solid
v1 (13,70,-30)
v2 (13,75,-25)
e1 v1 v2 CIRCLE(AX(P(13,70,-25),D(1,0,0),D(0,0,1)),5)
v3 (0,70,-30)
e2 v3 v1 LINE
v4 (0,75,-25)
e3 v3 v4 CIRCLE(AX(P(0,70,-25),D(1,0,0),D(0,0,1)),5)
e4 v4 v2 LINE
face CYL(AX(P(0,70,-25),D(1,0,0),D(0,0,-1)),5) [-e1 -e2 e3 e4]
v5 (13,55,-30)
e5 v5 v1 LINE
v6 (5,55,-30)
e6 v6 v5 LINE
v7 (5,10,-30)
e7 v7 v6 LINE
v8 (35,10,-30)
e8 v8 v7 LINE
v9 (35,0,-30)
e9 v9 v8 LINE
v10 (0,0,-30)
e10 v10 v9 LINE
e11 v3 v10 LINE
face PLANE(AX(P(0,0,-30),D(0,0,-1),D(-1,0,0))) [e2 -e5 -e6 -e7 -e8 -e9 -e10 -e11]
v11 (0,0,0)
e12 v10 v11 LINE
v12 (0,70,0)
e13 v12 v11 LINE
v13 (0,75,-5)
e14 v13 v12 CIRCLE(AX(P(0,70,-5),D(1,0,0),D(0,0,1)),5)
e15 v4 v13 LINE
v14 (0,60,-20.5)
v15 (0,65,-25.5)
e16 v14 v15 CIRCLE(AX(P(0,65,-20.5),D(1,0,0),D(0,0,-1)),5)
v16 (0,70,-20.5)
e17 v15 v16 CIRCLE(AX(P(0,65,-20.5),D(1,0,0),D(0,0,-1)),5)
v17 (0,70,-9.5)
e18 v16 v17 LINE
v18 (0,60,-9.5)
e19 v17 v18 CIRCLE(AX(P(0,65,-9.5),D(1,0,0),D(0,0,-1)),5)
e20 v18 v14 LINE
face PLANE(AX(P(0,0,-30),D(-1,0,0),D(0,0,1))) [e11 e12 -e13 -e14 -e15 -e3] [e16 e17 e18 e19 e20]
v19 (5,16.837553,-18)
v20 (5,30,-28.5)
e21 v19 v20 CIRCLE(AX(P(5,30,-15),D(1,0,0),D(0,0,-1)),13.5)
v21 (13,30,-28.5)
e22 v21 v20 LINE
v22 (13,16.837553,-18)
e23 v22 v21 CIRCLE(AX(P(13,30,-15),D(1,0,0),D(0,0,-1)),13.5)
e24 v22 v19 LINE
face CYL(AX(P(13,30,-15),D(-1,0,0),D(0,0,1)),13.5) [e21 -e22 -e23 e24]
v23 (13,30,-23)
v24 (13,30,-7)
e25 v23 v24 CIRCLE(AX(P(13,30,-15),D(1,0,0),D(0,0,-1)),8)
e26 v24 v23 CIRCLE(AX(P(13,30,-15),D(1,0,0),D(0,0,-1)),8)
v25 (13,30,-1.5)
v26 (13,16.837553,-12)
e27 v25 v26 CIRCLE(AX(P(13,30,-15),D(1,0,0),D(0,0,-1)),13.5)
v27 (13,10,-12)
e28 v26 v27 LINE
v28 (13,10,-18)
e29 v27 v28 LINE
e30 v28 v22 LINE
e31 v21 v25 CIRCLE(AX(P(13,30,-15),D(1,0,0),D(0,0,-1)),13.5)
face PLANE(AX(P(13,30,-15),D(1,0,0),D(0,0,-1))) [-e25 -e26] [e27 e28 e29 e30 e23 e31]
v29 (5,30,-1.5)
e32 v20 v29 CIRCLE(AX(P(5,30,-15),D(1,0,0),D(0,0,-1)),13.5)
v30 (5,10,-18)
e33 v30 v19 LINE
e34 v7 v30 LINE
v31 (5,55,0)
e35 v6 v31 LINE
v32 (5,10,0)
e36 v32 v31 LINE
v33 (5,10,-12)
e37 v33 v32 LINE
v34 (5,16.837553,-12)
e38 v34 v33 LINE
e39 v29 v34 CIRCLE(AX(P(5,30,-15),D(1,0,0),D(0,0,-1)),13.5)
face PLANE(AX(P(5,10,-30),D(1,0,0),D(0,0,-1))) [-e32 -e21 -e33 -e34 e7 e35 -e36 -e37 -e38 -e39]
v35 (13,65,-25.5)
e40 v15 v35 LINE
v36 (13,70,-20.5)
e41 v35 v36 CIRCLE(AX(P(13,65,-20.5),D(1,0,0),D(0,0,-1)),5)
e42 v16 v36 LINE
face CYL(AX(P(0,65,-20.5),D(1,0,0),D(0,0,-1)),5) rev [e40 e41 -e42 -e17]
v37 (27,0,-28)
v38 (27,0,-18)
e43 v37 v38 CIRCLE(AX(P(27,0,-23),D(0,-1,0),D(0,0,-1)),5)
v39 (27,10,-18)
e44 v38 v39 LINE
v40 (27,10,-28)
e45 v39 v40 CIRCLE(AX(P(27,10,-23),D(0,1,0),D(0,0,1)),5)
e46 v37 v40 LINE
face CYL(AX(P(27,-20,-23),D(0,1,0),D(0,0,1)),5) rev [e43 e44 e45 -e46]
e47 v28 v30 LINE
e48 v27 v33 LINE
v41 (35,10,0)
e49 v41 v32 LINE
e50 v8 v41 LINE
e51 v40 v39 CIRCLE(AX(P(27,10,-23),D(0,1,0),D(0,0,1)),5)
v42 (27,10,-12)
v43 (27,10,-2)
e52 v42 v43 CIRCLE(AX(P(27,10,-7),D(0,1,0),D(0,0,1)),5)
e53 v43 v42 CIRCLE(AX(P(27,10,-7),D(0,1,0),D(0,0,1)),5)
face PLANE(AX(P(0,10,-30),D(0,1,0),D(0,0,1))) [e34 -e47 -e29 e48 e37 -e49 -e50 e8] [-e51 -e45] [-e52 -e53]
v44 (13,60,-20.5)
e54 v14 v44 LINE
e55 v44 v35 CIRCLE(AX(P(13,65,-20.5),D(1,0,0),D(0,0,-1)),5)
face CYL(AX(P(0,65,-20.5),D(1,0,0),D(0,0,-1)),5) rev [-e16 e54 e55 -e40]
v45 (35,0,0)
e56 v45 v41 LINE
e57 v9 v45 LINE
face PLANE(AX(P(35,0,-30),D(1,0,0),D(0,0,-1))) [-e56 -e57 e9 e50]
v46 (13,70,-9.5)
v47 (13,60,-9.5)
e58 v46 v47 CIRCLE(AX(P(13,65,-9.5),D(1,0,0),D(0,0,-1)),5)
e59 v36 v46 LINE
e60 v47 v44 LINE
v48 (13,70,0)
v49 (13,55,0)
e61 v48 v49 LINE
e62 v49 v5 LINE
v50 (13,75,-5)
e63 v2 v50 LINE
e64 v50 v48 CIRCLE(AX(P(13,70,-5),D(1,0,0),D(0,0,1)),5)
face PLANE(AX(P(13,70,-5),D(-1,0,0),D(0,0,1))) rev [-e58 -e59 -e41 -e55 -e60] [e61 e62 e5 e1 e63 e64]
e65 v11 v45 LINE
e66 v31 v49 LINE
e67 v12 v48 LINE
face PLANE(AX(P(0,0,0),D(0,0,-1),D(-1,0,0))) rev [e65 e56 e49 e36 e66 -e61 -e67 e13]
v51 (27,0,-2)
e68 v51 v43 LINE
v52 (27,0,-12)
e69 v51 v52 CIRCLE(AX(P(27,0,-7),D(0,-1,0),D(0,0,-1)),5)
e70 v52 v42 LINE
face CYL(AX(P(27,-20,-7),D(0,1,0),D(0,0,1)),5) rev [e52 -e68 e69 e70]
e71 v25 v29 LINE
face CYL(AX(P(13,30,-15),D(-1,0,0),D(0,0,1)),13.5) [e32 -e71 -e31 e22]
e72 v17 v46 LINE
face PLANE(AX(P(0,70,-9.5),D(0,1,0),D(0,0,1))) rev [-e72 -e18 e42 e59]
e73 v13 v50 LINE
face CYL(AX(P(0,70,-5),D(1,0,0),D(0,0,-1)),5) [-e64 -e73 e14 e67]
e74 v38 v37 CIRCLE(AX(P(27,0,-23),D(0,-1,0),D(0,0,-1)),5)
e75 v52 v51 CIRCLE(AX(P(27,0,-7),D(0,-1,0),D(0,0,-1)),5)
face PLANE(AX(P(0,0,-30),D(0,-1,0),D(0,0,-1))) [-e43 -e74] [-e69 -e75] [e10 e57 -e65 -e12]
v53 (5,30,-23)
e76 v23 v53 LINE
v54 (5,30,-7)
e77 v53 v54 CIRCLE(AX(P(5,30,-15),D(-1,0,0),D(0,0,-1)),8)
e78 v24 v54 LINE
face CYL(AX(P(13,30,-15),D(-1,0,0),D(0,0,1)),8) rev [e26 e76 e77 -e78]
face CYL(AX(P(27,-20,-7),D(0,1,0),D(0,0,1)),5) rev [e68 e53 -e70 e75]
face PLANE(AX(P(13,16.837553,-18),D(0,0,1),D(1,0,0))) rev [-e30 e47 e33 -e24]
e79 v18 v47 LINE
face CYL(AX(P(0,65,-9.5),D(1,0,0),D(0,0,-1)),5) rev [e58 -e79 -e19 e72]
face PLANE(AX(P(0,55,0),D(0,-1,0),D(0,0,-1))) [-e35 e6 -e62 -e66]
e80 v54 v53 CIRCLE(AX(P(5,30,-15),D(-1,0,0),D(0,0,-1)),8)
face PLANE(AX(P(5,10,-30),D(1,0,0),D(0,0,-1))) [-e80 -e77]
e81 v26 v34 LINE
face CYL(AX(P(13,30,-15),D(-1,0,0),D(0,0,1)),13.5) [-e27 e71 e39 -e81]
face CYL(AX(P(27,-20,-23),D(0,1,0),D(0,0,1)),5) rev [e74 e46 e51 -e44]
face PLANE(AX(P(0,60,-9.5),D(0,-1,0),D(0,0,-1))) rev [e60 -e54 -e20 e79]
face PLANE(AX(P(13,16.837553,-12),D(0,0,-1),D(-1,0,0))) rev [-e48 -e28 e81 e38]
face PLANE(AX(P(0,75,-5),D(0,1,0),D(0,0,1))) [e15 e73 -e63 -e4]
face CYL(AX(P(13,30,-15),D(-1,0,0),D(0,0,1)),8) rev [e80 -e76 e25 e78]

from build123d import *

# Parameters (mm, degrees)
BASE_PLATE_SKETCH_W     = 35
BASE_PLATE_SKETCH_H     = 10
BASE_PLATE_DEPTH        = 30
UPRIGHT_WALL_SKETCH_W   = 5
UPRIGHT_WALL_SKETCH_H   = 45
UPRIGHT_WALL_DEPTH      = 30
MOUNTING_HOLES_SKETCH_R = 5
MOUNTING_HOLES_2X_DEPTH = 30
TOP_LUG_DEPTH           = 8
TOP_LUG_DEPTH_BACK      = 5
LUG_SLOT_DEPTH          = 84.719770664
RING_BOSS_SKETCH_R      = 8
RING_BOSS_DEPTH         = 8


with BuildPart() as part:
    # Base Plate Sketch → Base Plate (new body)
    with BuildSketch(Plane.XY):
        with Locations((17.5, 5)):
            Rectangle(BASE_PLATE_SKETCH_W, BASE_PLATE_SKETCH_H)
    extrude(amount=-BASE_PLATE_DEPTH)

    # Upright Wall Sketch → Upright Wall (add)
    with BuildSketch(Plane.XY):
        with Locations((2.5, 32.5)):
            Rectangle(UPRIGHT_WALL_SKETCH_W, UPRIGHT_WALL_SKETCH_H)
    extrude(amount=-UPRIGHT_WALL_DEPTH)

    # Mounting Holes Sketch → Mounting Holes 2x (cut)
    with BuildSketch(Plane(origin=(0, 10, 0), x_dir=(1, 0, 0), z_dir=(0, 1, 0))):
        with Locations(Location((27, 23, 0), (0, 0, 270))):
            Circle(MOUNTING_HOLES_SKETCH_R)
        with Locations(Location((27, 7, 0), (0, 0, 270))):
            Circle(MOUNTING_HOLES_SKETCH_R)
    extrude(amount=-MOUNTING_HOLES_2X_DEPTH, mode=Mode.SUBTRACT)

    # Top Lug Sketch → Top Lug (add, two sides: drawn at the far end of the back side and taken through both)
    with BuildSketch(Plane(origin=(5, 0, 0), x_dir=(0, 0, -1), z_dir=(1, 0, 0)).offset(-TOP_LUG_DEPTH_BACK)):
        with BuildLine():
            Line((0, 55), (30, 55))
            Line((30, 55), (30, 70))
            ThreePointArc((30, 70), (28.535533906, 73.535533906), (25, 75))
            Line((25, 75), (5, 75))
            ThreePointArc((5, 75), (1.464466094, 73.535533906), (0, 70))
            Line((0, 70), (0, 55))
        make_face()
    extrude(amount=TOP_LUG_DEPTH + TOP_LUG_DEPTH_BACK)

    # Lug Slot Sketch → Lug Slot (cut, through all)
    with BuildSketch(Plane(origin=(13, 0, 0), x_dir=(0, 0, -1), z_dir=(1, 0, 0))):
        with BuildLine():
            Line((9.5, 70), (20.5, 70))
            ThreePointArc((20.5, 70), (25.5, 65), (20.5, 60))
            Line((20.5, 60), (9.5, 60))
            ThreePointArc((9.5, 60), (4.5, 65), (9.5, 70))
        make_face()
    extrude(amount=-LUG_SLOT_DEPTH, mode=Mode.SUBTRACT)

    # Ring Boss Sketch → Ring Boss (add)
    with BuildSketch(Plane(origin=(5, 0, 0), x_dir=(0, 0, -1), z_dir=(1, 0, 0))):
        with BuildLine():
            Line((12, 16.837553419), (12, 10))
            Line((12, 10), (18, 10))
            Line((18, 10), (18, 16.837553419))
            ThreePointArc((18, 16.837553419), (15, 43.5), (12, 16.837553419))
        make_face()
        with Locations((15, 30)):
            Circle(RING_BOSS_SKETCH_R, mode=Mode.SUBTRACT)
    extrude(amount=RING_BOSS_DEPTH)


solid = part.part
